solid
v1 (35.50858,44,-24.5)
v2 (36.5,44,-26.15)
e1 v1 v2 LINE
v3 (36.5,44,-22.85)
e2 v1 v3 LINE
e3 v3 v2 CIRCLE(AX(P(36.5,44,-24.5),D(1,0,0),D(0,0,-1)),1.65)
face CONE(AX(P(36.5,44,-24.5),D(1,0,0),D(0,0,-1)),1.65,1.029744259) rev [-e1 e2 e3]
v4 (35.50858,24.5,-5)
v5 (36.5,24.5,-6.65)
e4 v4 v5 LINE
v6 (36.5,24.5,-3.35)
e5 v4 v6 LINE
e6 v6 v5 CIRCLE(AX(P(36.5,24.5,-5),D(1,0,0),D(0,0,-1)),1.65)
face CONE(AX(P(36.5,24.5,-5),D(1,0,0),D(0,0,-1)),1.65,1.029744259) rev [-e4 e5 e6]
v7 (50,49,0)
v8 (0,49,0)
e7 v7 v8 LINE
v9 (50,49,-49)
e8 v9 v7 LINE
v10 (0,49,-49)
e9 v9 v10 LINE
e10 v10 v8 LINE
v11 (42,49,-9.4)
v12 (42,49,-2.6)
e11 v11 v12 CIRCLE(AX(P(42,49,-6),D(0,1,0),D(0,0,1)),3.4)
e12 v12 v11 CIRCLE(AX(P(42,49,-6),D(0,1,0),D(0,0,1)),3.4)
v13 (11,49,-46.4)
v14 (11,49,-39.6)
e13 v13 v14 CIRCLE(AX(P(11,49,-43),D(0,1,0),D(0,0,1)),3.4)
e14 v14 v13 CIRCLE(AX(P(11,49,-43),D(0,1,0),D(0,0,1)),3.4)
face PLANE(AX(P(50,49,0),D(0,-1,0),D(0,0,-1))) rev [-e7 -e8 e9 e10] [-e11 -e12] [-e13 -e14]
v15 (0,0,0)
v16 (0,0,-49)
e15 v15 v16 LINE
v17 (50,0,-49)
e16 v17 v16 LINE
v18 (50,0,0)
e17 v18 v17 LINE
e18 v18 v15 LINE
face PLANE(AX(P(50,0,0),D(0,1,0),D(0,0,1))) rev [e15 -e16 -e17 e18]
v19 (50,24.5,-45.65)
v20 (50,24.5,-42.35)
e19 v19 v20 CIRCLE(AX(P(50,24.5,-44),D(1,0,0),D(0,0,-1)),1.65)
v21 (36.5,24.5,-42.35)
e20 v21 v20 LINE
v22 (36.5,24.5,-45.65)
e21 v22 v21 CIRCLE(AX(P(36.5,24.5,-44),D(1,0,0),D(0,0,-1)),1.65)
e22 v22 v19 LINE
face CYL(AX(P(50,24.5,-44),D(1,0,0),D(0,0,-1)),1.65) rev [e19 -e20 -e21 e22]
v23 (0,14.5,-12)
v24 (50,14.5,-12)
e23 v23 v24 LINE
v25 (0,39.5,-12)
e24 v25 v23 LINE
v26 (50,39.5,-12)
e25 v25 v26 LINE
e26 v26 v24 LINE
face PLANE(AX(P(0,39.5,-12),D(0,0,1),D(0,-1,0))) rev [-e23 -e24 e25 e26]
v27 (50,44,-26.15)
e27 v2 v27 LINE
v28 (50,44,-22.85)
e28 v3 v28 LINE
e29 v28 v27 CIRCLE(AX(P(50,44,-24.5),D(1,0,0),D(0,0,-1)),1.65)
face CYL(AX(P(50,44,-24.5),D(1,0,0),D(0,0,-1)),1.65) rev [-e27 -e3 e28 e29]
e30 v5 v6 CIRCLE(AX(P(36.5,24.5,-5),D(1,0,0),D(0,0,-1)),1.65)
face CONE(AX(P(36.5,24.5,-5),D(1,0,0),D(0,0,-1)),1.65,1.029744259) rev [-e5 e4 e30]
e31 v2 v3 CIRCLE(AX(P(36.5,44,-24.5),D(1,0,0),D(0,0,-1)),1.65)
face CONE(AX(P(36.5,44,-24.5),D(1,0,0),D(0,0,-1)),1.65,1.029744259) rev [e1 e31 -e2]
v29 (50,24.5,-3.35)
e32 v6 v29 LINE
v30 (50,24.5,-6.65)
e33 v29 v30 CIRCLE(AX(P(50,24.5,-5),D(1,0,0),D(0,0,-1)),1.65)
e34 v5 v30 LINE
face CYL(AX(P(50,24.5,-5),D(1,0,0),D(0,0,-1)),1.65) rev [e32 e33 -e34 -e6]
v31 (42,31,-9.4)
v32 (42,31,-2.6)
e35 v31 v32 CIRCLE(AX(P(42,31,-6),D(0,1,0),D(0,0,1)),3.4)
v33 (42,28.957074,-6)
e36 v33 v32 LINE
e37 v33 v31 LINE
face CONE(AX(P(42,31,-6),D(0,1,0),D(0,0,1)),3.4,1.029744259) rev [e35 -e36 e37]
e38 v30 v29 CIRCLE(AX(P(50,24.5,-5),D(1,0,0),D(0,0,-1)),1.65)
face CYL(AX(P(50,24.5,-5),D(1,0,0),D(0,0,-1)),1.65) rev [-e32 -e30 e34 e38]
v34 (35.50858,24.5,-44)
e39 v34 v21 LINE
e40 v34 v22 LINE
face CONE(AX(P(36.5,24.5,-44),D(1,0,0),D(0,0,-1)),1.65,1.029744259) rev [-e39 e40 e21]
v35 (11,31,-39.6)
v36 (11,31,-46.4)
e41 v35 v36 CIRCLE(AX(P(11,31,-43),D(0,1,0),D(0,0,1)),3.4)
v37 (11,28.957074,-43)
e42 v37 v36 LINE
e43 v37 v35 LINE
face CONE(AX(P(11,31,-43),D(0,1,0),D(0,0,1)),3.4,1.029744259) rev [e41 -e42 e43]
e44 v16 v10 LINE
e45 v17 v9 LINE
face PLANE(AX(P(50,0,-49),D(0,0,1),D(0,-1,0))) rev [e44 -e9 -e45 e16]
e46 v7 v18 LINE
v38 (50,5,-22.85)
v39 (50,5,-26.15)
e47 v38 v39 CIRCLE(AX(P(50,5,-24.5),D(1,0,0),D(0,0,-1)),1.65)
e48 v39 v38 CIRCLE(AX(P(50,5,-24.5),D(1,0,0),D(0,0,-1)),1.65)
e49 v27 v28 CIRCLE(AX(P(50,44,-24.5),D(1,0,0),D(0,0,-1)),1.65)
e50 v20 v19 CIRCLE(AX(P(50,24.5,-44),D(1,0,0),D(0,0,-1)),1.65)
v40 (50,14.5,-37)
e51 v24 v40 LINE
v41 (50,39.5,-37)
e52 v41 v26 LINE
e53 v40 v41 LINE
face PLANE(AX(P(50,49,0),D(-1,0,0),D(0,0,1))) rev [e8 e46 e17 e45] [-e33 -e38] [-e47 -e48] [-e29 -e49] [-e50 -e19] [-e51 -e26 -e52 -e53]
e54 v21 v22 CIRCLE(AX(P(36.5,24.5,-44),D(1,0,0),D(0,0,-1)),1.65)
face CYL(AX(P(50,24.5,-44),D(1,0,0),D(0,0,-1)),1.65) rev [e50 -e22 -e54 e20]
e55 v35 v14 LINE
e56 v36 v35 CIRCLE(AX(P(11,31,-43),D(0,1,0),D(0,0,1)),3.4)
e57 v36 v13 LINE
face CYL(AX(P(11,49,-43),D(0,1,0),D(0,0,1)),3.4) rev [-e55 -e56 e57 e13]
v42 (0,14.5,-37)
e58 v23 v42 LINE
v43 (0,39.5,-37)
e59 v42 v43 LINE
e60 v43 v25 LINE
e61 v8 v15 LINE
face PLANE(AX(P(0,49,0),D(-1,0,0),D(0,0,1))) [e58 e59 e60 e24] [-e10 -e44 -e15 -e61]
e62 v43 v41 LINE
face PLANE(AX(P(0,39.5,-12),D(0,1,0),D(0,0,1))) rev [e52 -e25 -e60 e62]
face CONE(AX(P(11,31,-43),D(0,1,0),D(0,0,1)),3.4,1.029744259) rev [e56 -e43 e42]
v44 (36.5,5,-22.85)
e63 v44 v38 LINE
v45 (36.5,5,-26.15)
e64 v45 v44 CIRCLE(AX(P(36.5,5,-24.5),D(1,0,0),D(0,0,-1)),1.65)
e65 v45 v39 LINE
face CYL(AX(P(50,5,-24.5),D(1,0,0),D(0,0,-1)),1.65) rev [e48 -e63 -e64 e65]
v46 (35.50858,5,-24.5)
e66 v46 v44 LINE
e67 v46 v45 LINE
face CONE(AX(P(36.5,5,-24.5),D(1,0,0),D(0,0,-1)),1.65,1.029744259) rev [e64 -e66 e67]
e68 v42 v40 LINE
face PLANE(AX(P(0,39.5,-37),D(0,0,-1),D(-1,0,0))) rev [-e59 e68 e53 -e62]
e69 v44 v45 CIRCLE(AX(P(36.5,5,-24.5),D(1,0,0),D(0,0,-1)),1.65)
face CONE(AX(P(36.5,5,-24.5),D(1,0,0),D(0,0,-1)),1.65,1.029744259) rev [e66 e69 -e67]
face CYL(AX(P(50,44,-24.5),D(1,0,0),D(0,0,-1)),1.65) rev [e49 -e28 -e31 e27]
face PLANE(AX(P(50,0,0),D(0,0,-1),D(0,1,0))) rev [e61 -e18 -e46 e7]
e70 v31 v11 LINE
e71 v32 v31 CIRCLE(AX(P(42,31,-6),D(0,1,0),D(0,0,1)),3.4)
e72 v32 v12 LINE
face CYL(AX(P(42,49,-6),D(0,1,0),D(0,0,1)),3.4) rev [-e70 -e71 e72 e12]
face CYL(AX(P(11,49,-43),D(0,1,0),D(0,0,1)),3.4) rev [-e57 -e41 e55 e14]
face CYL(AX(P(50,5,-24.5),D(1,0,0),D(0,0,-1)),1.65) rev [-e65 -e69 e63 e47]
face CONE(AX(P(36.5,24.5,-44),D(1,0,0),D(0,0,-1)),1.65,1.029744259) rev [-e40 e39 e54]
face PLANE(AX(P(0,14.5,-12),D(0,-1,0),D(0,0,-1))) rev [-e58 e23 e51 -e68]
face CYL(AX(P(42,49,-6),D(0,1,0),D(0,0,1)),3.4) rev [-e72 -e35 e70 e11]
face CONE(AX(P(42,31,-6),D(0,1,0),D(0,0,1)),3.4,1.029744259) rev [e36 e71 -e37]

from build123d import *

# Parameters (mm, degrees)
SKETCH_2_W             = 49
SKETCH_2_H             = 49
EXTRUDE_2_DEPTH        = 50
SKETCH_3_W             = 25
SKETCH_3_H             = 25
CUT_EXTRUDE_1_DEPTH    = 50
HOLE_WIZARD_M4_1_D     = 3.3
HOLE_WIZARD_M4_1_DEPTH = 13.5
HOLE_WIZARD_M4_1_TIP   = 0.991420021
HOLE_WIZARD_M8_1_D     = 6.8
HOLE_WIZARD_M8_1_DEPTH = 18
HOLE_WIZARD_M8_1_TIP   = 2.042926105


with BuildPart() as part:
    # 草图2 → 凸台-拉伸2 (new body)
    with BuildSketch(Plane(origin=(0, 0, 0), x_dir=(0, 0, -1), z_dir=(1, 0, 0))):
        with Locations((24.5, 24.5)):
            Rectangle(SKETCH_2_W, SKETCH_2_H)
    extrude(amount=EXTRUDE_2_DEPTH)

    # 草图3 → 切除-拉伸1 (cut)
    with BuildSketch(Plane(origin=(50, 0, 0), x_dir=(0, 0, -1), z_dir=(1, 0, 0))):
        with Locations((24.5, 27)):
            Rectangle(SKETCH_3_W, SKETCH_3_H)
    extrude(amount=-CUT_EXTRUDE_1_DEPTH, mode=Mode.SUBTRACT)

    # M4 螺纹孔1
    with Locations(Plane(origin=(50, 0, 0), x_dir=(0, 0, -1), z_dir=(1, 0, 0))):
        with Locations((24.5, 44), (5, 24.5), (24.5, 5), (44, 24.5)):
            Hole(HOLE_WIZARD_M4_1_D / 2, depth=HOLE_WIZARD_M4_1_DEPTH)
            with Locations((0, 0, -(HOLE_WIZARD_M4_1_DEPTH + HOLE_WIZARD_M4_1_TIP / 2))):  # 118° drill point
                Cone(0, HOLE_WIZARD_M4_1_D / 2, HOLE_WIZARD_M4_1_TIP, mode=Mode.SUBTRACT)

    # M8 螺纹孔1
    with Locations(Plane(origin=(0, 49, 0), x_dir=(-1, 0, 0), z_dir=(0, 1, 0))):
        with Locations((-42, -6), (-11, -43)):
            Hole(HOLE_WIZARD_M8_1_D / 2, depth=HOLE_WIZARD_M8_1_DEPTH)
            with Locations((0, 0, -(HOLE_WIZARD_M8_1_DEPTH + HOLE_WIZARD_M8_1_TIP / 2))):  # 118° drill point
                Cone(0, HOLE_WIZARD_M8_1_D / 2, HOLE_WIZARD_M8_1_TIP, mode=Mode.SUBTRACT)


solid = part.part
